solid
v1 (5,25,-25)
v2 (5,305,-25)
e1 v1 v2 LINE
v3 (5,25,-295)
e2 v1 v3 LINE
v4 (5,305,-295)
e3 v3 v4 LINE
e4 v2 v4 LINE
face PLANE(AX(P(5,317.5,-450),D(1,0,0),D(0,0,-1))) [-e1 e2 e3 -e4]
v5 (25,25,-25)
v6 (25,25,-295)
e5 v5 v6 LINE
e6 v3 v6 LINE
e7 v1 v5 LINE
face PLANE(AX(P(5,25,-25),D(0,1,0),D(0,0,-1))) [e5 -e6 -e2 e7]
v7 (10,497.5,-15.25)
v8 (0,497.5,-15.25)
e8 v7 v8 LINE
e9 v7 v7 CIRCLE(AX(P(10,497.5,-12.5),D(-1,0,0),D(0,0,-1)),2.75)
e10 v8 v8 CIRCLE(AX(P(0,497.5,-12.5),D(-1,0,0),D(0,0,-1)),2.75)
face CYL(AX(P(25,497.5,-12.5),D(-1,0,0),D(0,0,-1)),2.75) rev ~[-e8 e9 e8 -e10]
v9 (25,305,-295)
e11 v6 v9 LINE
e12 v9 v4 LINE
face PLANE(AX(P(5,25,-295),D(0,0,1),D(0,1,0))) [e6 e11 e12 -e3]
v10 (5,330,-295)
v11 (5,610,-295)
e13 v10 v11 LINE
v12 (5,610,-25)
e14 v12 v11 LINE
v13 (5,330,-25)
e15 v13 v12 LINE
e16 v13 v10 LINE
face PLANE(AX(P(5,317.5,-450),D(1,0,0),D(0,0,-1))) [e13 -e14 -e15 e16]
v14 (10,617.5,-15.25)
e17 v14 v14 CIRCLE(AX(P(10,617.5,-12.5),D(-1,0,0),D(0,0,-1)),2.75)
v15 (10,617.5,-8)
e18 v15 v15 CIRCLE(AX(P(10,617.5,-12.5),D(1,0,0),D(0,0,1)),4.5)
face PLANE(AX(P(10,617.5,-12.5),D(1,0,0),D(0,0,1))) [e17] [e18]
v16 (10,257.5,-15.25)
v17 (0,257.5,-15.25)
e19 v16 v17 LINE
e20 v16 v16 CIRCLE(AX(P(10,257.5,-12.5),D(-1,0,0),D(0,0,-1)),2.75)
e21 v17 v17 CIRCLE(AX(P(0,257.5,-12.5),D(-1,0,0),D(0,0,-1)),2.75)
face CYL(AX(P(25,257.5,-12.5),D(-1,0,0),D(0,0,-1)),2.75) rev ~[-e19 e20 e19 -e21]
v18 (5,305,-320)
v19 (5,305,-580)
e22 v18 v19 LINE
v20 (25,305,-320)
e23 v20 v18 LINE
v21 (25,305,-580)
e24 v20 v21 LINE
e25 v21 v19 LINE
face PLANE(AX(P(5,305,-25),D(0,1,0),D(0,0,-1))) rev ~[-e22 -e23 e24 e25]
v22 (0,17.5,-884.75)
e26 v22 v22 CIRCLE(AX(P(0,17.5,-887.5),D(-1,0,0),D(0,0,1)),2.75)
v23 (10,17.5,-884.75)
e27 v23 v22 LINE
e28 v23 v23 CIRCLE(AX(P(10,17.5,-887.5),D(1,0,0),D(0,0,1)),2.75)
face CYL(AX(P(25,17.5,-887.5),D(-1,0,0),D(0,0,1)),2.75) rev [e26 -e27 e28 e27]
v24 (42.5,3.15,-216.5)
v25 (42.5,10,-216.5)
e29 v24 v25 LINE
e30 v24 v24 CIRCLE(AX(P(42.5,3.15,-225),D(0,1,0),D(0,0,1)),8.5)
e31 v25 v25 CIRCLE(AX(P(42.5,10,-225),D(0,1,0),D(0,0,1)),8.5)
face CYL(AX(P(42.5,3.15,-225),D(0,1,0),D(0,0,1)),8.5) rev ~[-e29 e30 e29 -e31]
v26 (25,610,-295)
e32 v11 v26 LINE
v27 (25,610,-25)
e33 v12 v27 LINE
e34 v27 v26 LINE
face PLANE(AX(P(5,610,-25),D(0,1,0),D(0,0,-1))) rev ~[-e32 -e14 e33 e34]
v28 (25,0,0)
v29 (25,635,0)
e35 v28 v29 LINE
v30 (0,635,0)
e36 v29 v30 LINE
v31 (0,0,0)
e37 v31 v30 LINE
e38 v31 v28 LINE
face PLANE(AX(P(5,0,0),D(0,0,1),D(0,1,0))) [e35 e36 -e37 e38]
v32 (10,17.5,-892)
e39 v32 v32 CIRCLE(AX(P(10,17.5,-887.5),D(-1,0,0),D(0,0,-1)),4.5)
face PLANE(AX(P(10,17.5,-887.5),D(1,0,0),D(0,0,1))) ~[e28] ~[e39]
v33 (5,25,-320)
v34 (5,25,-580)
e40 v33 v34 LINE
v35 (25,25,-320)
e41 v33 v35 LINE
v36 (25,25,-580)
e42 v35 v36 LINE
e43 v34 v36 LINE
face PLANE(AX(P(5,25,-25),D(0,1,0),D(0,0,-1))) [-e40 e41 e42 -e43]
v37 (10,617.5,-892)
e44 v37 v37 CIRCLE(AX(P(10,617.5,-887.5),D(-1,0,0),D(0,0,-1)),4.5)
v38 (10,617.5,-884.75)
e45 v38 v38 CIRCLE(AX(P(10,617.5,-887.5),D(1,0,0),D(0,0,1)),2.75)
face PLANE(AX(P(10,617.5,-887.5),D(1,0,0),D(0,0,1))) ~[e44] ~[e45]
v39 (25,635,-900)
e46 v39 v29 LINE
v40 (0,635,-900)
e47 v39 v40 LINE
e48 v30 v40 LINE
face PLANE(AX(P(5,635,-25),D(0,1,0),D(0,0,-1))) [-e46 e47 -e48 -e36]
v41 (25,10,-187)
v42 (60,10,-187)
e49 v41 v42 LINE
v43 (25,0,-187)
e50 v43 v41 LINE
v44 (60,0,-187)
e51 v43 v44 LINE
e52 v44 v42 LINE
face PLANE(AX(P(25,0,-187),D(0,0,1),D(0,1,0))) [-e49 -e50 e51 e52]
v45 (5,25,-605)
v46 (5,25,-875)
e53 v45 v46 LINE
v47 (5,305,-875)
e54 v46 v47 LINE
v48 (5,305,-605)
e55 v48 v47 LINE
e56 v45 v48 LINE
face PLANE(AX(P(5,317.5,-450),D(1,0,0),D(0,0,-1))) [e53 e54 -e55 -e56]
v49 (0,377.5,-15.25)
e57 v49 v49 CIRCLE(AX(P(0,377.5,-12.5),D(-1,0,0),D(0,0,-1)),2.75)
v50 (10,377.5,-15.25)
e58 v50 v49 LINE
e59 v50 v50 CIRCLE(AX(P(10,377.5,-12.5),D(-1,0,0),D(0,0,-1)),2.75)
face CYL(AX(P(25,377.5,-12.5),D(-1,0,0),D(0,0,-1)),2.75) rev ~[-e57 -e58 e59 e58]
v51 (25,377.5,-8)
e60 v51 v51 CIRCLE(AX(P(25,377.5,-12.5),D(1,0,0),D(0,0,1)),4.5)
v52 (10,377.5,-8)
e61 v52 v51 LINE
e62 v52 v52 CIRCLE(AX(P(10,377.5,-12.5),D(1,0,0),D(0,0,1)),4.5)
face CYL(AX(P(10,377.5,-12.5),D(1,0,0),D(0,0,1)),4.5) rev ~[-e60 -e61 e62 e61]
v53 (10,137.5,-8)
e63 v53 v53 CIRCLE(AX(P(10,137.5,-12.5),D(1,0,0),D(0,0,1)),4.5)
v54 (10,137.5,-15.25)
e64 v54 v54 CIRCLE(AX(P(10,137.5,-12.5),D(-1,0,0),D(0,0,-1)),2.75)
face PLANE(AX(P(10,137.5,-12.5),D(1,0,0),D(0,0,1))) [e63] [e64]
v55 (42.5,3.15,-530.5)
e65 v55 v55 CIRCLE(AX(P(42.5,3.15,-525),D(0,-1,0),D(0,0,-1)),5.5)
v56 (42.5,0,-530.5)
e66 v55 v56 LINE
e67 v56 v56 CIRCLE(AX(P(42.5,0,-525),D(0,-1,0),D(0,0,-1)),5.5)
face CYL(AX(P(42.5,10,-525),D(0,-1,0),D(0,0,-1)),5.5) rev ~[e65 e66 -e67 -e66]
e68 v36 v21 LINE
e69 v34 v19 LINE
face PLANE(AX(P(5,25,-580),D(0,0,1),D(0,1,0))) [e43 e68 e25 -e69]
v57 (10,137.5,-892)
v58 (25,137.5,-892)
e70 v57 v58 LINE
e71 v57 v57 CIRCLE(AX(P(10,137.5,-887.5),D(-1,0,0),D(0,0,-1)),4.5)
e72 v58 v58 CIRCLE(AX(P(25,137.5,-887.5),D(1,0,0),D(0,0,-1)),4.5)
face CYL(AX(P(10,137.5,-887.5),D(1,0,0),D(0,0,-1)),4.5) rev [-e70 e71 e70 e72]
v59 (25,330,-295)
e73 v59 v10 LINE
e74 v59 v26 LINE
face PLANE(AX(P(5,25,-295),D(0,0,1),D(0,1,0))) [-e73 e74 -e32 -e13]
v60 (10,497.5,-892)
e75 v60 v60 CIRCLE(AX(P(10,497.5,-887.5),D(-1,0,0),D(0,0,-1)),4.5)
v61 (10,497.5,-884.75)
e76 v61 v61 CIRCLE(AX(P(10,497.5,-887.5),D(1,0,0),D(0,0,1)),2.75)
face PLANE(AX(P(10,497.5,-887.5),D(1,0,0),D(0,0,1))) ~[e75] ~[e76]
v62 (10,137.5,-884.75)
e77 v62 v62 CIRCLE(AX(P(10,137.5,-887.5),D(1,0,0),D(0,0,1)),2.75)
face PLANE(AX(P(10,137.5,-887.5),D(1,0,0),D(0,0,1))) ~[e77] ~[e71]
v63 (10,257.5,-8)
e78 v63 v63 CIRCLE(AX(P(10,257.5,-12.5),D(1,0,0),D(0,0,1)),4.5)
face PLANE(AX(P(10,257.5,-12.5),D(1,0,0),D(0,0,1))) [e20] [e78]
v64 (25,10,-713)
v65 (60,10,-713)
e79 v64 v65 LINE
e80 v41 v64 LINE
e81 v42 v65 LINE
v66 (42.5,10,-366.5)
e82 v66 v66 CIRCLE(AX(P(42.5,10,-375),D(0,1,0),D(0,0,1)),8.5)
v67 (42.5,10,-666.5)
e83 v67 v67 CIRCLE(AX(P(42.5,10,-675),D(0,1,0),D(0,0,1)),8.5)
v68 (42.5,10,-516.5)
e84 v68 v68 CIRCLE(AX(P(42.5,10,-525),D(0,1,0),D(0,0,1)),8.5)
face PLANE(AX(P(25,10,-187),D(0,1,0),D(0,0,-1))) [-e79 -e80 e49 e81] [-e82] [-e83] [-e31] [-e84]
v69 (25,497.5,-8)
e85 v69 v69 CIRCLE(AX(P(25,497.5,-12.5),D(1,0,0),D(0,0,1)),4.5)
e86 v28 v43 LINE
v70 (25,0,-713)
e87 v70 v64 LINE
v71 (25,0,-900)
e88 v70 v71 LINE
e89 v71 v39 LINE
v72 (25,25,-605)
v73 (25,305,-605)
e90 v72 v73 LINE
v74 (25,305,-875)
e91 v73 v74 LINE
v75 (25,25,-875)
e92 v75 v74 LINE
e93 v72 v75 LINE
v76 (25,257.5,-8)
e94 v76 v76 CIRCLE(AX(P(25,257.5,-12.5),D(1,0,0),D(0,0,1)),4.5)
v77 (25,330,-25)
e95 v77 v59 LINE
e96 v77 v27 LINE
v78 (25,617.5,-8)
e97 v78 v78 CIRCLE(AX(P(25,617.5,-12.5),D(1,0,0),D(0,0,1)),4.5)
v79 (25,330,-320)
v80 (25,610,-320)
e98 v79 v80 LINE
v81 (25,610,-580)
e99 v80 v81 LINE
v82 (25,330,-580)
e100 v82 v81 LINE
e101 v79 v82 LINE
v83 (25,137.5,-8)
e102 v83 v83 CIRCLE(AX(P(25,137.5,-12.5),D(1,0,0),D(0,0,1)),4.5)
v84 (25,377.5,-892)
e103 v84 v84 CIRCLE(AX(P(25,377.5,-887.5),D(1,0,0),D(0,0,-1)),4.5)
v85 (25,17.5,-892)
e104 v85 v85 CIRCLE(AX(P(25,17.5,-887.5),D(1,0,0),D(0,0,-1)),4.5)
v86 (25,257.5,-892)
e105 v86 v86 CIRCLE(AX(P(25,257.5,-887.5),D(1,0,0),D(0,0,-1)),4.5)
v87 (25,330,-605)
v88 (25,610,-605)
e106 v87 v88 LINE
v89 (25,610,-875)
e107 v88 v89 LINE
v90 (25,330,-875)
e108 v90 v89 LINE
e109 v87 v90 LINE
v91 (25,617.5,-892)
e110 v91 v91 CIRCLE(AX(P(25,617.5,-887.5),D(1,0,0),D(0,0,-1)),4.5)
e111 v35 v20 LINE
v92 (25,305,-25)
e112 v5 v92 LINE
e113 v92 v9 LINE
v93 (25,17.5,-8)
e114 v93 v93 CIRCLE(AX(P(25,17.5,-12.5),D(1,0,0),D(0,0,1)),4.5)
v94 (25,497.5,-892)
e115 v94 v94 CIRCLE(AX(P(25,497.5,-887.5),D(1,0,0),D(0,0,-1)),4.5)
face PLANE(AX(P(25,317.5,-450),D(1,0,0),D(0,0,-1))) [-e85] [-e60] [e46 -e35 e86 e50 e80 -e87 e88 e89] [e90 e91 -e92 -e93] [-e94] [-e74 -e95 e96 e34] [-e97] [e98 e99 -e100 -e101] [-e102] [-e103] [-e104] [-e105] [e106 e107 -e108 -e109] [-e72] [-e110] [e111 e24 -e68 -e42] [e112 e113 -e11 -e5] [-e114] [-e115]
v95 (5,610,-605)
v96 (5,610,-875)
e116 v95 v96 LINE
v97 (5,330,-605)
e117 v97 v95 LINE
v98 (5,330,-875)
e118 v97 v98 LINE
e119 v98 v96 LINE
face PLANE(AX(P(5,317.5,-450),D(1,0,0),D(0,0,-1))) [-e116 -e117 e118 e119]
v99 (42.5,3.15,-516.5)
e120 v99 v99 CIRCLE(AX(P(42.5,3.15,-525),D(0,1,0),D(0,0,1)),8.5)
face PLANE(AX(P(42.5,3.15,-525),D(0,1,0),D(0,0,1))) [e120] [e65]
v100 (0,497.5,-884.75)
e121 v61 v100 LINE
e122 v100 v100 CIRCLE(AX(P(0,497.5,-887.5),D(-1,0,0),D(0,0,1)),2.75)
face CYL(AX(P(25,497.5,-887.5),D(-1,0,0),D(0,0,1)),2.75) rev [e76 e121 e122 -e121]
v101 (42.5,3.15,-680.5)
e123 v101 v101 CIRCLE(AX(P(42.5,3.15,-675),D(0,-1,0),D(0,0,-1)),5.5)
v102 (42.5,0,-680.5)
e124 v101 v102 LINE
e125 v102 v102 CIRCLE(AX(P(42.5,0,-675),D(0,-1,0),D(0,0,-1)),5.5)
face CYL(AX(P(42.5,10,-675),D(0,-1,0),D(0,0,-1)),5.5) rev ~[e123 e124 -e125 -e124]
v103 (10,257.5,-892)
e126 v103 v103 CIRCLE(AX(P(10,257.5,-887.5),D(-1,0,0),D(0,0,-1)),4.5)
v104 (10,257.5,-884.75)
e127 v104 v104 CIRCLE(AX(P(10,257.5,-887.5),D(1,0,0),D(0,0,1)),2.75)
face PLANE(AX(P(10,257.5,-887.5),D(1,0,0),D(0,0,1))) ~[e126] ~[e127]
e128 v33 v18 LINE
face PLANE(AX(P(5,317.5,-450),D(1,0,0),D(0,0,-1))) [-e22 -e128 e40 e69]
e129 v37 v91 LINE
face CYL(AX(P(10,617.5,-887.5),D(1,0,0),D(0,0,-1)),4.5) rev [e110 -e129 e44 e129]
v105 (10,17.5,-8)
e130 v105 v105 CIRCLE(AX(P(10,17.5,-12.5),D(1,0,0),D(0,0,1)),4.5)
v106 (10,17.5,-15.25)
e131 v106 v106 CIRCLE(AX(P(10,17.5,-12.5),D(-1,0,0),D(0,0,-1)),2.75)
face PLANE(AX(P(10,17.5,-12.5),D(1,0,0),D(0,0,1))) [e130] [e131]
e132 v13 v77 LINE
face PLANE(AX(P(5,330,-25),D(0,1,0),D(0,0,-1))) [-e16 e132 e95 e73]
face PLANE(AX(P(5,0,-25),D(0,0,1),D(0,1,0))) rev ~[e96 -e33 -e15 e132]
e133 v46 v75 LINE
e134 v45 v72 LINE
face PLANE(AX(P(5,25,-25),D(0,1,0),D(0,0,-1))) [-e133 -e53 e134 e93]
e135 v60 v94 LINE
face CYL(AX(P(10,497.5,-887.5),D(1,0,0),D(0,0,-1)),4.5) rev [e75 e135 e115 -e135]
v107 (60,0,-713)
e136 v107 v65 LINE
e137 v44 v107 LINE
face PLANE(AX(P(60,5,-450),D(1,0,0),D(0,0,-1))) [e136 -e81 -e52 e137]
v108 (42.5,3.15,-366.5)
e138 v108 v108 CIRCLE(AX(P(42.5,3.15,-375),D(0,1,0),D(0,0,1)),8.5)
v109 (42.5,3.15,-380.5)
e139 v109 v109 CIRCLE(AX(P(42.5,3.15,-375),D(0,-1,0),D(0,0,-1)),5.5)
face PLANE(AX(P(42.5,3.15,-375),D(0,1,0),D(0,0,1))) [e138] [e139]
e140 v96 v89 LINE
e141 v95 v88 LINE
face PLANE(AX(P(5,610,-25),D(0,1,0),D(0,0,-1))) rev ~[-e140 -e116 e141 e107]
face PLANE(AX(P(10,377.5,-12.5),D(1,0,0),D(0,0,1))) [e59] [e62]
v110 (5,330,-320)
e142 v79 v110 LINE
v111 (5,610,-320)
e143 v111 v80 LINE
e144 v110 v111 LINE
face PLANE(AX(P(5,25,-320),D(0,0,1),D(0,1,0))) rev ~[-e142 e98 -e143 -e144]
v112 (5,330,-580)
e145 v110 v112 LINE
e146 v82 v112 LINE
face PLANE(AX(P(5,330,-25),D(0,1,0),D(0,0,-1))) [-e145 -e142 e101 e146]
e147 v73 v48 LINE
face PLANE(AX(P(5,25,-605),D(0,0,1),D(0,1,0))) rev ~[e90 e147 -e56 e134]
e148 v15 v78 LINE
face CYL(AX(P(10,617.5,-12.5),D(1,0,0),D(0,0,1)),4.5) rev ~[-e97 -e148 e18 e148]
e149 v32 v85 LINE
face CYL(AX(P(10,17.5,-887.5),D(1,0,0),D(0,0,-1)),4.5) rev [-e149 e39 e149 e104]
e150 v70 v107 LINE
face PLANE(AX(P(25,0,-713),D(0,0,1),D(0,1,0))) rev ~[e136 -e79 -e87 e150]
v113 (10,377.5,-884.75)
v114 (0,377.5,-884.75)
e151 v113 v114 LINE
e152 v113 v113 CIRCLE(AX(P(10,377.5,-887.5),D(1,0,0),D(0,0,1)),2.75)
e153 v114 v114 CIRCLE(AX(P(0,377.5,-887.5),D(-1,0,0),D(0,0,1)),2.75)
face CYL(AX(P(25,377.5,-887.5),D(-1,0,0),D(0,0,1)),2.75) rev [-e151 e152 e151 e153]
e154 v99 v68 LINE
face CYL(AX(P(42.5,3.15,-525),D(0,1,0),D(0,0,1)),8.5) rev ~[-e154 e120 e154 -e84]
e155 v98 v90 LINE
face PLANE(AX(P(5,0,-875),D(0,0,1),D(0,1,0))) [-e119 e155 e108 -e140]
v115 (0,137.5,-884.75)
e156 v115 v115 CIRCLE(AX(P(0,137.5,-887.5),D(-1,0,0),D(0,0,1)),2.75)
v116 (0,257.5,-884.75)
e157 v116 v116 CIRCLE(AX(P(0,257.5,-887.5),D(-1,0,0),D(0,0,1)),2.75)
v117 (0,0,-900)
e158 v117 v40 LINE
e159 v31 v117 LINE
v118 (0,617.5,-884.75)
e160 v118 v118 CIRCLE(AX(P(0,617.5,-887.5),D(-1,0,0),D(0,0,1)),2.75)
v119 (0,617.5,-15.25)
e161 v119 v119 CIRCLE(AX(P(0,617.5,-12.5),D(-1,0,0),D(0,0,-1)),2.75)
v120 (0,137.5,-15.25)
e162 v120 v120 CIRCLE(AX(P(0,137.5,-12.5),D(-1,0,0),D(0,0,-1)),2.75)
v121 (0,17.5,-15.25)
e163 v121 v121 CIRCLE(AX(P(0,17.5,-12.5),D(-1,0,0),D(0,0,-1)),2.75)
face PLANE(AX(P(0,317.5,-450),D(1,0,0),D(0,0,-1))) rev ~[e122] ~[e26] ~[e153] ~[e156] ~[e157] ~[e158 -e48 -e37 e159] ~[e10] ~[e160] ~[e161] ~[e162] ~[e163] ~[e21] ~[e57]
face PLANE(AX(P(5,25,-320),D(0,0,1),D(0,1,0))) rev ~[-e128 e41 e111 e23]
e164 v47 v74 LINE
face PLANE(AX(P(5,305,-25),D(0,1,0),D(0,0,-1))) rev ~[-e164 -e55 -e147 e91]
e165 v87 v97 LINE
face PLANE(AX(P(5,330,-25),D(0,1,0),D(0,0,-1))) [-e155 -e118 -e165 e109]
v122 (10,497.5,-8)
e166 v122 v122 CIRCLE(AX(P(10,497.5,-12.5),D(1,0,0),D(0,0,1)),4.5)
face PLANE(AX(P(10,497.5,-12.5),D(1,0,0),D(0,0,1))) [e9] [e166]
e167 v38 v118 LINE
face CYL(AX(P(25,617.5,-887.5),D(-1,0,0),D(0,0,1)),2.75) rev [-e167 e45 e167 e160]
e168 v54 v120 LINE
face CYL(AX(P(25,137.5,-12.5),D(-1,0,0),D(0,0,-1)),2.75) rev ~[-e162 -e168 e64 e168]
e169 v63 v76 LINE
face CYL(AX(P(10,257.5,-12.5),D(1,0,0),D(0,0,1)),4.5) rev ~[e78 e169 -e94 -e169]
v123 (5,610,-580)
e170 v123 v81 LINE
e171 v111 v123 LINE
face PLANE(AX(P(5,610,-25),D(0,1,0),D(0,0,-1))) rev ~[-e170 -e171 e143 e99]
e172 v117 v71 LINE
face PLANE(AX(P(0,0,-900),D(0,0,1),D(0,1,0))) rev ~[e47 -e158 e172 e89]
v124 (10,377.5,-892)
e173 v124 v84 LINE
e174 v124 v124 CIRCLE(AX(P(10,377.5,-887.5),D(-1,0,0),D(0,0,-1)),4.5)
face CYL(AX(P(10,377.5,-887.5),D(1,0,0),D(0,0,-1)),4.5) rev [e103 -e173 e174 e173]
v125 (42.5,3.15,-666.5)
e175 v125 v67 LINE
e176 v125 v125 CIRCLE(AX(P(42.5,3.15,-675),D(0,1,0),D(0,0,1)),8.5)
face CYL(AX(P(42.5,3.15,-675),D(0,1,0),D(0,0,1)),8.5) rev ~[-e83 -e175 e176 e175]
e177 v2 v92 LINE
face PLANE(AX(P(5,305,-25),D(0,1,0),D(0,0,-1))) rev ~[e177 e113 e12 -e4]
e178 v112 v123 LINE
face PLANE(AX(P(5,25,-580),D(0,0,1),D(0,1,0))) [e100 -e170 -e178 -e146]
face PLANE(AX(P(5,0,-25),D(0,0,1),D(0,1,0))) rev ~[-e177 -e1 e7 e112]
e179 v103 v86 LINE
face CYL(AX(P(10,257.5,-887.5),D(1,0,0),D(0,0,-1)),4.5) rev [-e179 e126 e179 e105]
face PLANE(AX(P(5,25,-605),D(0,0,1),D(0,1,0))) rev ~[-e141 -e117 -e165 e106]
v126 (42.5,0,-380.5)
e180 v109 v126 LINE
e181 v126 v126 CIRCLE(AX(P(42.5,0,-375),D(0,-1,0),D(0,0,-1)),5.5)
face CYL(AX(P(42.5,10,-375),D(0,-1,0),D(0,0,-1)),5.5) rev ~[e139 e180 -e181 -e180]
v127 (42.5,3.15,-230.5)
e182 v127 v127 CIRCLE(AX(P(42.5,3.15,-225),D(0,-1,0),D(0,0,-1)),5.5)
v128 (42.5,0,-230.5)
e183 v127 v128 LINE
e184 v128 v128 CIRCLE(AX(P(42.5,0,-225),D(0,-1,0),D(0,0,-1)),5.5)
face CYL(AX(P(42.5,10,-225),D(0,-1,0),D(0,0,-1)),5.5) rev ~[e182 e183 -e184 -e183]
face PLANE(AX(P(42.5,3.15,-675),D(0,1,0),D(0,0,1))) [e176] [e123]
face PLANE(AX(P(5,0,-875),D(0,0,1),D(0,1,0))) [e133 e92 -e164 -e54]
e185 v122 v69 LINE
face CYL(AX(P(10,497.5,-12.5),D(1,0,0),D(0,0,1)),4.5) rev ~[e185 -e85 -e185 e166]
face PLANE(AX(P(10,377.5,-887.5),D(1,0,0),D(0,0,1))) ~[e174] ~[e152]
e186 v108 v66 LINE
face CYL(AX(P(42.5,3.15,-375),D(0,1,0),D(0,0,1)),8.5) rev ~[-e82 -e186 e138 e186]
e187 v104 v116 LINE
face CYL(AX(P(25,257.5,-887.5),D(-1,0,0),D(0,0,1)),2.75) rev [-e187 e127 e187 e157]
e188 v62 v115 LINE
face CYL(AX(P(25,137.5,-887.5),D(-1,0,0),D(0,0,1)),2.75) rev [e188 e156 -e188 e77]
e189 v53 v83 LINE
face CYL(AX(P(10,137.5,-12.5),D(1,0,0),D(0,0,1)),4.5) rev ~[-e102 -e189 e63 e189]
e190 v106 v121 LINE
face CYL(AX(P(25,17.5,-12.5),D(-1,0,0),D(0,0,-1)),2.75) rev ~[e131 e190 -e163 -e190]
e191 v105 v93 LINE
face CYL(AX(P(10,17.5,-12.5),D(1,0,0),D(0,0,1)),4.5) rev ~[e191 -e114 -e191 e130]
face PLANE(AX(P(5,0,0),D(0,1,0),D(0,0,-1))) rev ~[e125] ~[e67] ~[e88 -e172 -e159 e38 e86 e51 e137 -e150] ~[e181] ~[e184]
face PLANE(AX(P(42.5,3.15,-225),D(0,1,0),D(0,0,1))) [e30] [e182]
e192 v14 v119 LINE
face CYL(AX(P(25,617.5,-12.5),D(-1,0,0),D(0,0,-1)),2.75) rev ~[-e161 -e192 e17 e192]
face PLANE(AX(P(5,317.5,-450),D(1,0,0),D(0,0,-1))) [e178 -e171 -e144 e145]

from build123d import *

# Parameters (mm, degrees)
SKETCH_1_W                = 900
SKETCH_1_H                = 635
EXTRUDE_1_DEPTH           = 5
SKETCH_2_W                = 25
SKETCH_2_H                = 635
EXTRUDE_2_DEPTH           = 20
SKETCH_4_W                = 850
SKETCH_4_H                = 25
EXTRUDE_3_DEPTH           = 20
SKETCH_5_W                = 25
SKETCH_5_H                = 585
EXTRUDE_4_DEPTH           = 20
SKETCH_6_W                = 850
SKETCH_6_H                = 25
EXTRUDE_5_DEPTH           = 20
SKETCH_7_W                = 526
SKETCH_7_H                = 10
EXTRUDE_6_DEPTH           = 35
HOLE_WIZARD_1_D           = 11
HOLE_WIZARD_1_CBORE_D     = 17
HOLE_WIZARD_1_CBORE_DEPTH = 6.85
HOLE_WIZARD_2_D           = 5.5
HOLE_WIZARD_2_CBORE_D     = 9
HOLE_WIZARD_2_CBORE_DEPTH = 15


with BuildPart() as part:
    # 草图1 → 拉伸1 (new body)
    with BuildSketch(Plane(origin=(0, 0, 0), x_dir=(0, 0, -1), z_dir=(1, 0, 0))):
        with Locations((450, 317.5)):
            Rectangle(SKETCH_1_W, SKETCH_1_H)
    extrude(amount=EXTRUDE_1_DEPTH)

    # 草图2 → 拉伸2 (add)
    with BuildSketch(Plane(origin=(5, 0, 0), x_dir=(0, 0, -1), z_dir=(1, 0, 0))):
        with Locations((12.5, 317.5)):
            Rectangle(SKETCH_2_W, SKETCH_2_H)
        with Locations((887.5, 317.5)):
            Rectangle(SKETCH_2_W, SKETCH_2_H)
    extrude(amount=EXTRUDE_2_DEPTH)

    # 草图4 → 拉伸3 (add)
    with BuildSketch(Plane(origin=(5, 0, 0), x_dir=(0, 0, -1), z_dir=(1, 0, 0))):
        with Locations((450, 622.5)):
            Rectangle(SKETCH_4_W, SKETCH_4_H)
        with Locations((450, 12.5)):
            Rectangle(SKETCH_4_W, SKETCH_4_H)
    extrude(amount=EXTRUDE_3_DEPTH)

    # 草图5 → 拉伸4 (add)
    with BuildSketch(Plane(origin=(5, 0, 0), x_dir=(0, 0, -1), z_dir=(1, 0, 0))):
        with Locations((307.5, 317.5)):
            Rectangle(SKETCH_5_W, SKETCH_5_H)
        with Locations((592.5, 317.5)):
            Rectangle(SKETCH_5_W, SKETCH_5_H)
    extrude(amount=EXTRUDE_4_DEPTH)

    # 草图6 → 拉伸5 (add)
    with BuildSketch(Plane(origin=(5, 0, 0), x_dir=(0, 0, -1), z_dir=(1, 0, 0))):
        with Locations((450, 317.5)):
            Rectangle(SKETCH_6_W, SKETCH_6_H)
    extrude(amount=EXTRUDE_5_DEPTH)

    # 草图7 → 拉伸6 (add)
    with BuildSketch(Plane(origin=(25, 0, 0), x_dir=(0, 0, -1), z_dir=(1, 0, 0))):
        with Locations((450, 5)):
            Rectangle(SKETCH_7_W, SKETCH_7_H)
    extrude(amount=EXTRUDE_6_DEPTH)

    # 孔1 (through all)
    with Locations(Plane(origin=(42.5, 10, -675), x_dir=(0, 0, 1), z_dir=(0, 1, 0))):
        with Locations((0, 0), (150, 0), (300, 0), (450, 0)):
            CounterBoreHole(HOLE_WIZARD_1_D / 2, HOLE_WIZARD_1_CBORE_D / 2, HOLE_WIZARD_1_CBORE_DEPTH)

    # 孔2 (through all)
    with Locations(Plane(origin=(25, 617.5, -12.5), x_dir=(0, 0, 1), z_dir=(1, 0, 0))):
        with Locations((0, 0), (0, 120), (0, 240), (0, 360), (0, 480), (0, 600)):
            hole_wizard_2 = CounterBoreHole(HOLE_WIZARD_2_D / 2, HOLE_WIZARD_2_CBORE_D / 2, HOLE_WIZARD_2_CBORE_DEPTH)

    # 镜向1: 孔2 across plane
    add(hole_wizard_2.mirror(Plane.XY.offset(-450)), mode=Mode.SUBTRACT)


solid = part.part
